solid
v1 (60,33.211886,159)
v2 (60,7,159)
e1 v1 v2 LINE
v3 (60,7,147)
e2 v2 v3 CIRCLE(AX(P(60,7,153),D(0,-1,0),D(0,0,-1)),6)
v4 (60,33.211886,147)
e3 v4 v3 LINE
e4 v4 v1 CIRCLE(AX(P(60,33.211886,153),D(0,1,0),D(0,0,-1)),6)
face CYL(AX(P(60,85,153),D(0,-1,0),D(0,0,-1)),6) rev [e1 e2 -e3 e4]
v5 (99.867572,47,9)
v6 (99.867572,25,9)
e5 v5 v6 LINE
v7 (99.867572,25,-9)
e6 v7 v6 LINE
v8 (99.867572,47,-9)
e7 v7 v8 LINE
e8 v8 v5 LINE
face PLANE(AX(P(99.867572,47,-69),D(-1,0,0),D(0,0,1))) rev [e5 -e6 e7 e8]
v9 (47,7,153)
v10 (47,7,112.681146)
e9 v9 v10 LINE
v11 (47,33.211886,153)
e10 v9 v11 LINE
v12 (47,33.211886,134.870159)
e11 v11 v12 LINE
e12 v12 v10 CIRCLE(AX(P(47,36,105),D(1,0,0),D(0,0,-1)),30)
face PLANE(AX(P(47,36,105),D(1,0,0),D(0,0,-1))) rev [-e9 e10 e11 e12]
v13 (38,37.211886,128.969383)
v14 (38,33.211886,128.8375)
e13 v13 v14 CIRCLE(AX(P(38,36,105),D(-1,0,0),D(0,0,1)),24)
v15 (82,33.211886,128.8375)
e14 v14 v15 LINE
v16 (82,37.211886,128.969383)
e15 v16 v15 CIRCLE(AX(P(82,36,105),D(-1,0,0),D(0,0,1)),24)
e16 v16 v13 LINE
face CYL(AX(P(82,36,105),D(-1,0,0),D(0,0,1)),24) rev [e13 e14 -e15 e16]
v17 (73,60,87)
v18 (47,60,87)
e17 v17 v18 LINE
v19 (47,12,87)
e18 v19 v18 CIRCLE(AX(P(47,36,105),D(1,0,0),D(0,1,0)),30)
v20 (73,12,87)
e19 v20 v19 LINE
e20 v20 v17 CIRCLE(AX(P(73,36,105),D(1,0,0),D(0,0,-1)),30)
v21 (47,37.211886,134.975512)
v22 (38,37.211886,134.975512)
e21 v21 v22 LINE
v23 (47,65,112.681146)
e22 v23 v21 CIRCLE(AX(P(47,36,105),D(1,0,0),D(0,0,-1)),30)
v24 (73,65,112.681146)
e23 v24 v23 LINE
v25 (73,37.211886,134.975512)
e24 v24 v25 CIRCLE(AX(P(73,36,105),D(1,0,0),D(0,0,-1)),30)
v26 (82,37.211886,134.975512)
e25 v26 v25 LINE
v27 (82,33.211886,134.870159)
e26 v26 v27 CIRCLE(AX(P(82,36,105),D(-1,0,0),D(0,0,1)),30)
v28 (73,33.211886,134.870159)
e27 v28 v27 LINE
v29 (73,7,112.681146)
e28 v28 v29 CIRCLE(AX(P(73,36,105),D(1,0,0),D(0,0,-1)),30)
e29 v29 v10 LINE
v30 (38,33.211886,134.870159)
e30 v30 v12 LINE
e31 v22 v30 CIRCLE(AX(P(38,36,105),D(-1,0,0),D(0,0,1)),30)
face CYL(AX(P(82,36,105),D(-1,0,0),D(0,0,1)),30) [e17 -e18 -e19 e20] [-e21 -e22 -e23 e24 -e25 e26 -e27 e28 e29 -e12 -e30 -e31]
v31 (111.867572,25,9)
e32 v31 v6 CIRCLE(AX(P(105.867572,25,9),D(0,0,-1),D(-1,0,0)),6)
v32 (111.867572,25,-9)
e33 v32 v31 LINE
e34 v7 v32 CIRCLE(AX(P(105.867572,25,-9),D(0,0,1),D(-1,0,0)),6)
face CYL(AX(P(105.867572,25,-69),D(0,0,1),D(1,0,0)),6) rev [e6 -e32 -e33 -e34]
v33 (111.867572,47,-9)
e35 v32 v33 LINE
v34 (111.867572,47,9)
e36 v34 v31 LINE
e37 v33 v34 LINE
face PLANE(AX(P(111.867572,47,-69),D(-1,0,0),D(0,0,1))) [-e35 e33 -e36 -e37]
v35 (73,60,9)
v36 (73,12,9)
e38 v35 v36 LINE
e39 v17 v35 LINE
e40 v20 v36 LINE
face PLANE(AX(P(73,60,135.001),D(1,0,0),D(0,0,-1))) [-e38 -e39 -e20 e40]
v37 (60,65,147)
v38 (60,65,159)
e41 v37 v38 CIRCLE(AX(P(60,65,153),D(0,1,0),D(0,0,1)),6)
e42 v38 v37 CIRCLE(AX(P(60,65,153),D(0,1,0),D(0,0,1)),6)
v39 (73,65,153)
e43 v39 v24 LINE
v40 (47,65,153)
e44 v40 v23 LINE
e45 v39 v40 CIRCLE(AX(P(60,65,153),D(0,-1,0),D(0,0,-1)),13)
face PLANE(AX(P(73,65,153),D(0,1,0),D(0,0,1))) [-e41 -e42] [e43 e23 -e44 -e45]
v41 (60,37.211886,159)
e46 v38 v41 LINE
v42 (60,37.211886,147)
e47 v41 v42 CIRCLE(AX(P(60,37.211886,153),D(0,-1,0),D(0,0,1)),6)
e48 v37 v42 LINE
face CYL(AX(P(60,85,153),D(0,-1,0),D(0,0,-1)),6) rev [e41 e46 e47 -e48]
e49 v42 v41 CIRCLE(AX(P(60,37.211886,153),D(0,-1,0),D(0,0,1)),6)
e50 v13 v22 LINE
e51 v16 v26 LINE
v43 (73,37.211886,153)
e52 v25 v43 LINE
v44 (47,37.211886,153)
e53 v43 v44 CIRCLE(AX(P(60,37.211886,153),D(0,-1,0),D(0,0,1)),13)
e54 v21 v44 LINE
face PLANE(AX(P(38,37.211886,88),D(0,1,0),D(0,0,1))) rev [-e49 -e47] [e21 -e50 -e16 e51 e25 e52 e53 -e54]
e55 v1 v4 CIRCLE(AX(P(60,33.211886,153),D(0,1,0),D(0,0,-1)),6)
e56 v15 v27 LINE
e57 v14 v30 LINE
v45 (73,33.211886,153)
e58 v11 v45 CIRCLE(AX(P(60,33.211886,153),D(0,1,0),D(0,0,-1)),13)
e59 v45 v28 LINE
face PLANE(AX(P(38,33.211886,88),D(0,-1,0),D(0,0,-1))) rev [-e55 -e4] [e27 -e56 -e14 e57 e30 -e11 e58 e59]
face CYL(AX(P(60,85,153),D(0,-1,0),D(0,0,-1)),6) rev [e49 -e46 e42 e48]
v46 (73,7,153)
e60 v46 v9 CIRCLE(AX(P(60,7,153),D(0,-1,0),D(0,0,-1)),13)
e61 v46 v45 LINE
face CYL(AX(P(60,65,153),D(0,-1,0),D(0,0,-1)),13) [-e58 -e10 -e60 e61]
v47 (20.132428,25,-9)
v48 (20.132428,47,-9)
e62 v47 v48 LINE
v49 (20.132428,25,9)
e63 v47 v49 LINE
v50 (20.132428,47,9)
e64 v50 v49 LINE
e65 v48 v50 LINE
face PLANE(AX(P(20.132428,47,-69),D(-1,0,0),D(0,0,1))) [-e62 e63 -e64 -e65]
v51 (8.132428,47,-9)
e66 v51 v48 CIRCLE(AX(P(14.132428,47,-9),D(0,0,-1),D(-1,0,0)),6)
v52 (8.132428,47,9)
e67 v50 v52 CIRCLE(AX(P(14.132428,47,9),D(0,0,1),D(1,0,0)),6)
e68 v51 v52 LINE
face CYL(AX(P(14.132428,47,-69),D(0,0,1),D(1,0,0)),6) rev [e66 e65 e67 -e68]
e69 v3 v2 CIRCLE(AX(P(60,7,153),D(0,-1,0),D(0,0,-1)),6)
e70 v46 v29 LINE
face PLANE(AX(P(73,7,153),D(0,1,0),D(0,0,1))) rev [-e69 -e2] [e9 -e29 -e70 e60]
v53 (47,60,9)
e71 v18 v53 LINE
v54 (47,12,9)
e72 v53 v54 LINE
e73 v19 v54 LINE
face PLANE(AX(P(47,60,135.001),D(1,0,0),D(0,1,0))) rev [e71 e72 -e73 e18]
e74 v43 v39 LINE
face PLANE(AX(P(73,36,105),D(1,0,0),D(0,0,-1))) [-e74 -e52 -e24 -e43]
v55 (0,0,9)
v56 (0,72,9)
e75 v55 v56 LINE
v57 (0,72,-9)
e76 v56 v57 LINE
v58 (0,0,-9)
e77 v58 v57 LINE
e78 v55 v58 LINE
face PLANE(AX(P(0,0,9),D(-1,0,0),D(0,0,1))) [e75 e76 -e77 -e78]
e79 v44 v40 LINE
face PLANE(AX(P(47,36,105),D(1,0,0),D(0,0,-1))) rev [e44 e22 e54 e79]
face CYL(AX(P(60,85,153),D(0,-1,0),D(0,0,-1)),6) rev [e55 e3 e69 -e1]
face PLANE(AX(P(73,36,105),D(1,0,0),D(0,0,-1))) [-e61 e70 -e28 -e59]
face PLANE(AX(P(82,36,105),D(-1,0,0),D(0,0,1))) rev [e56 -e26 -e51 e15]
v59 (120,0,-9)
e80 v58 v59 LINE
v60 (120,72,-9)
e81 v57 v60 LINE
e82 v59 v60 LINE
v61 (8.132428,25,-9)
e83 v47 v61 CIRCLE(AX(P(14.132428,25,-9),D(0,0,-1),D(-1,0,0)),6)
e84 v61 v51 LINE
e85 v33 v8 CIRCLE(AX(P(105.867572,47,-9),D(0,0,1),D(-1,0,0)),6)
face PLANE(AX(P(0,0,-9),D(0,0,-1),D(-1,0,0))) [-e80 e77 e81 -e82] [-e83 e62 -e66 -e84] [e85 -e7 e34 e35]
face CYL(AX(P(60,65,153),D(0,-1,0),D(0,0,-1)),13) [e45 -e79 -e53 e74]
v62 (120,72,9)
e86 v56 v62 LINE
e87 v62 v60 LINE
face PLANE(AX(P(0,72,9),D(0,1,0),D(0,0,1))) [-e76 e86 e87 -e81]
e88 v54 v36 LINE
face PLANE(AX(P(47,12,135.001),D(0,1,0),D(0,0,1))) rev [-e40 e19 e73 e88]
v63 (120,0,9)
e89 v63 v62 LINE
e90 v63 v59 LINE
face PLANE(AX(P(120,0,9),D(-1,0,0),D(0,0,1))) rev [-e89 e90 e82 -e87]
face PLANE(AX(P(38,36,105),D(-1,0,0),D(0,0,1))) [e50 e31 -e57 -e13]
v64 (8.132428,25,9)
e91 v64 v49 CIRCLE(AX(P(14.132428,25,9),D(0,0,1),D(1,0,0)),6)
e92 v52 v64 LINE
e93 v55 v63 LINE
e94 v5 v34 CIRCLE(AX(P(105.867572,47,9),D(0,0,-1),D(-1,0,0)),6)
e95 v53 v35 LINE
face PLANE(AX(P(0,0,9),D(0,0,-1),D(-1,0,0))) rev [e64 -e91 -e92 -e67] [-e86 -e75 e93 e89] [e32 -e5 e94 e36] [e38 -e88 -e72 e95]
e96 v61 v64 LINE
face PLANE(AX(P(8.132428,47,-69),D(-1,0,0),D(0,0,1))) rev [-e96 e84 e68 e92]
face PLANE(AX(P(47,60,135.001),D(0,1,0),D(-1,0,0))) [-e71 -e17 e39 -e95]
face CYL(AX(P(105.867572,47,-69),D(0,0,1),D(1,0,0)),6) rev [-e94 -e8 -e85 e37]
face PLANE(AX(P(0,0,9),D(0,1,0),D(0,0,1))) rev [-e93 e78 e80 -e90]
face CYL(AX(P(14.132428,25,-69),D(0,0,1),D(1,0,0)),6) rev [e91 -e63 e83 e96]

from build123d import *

# Parameters (mm, degrees)
BASE_PLATE_SKETCH_W        = 120
BASE_PLATE_SKETCH_H        = 72
BASE_PLATE_120X72X18_DEPTH = 9
CLAMP_RING_SKETCH_R        = 30
CLAMP_RING_SKETCH_R_2      = 24
CLAMP_RING_DEPTH           = 22
ARM_REACH                  = 190.308
ARM_END_RADIUS             = 30
ARM_PROFILE_SKETCH_W       = 26
ARM_PROFILE_SKETCH_H       = 48
CLAMP_LUG_DEPTH            = 13
CLAMP_LUG_EXTENSION_DEPTH  = 58
CLAMP_BOLT_HOLE_SKETCH_R   = 6
CLAMP_BOLT_HOLE_12_DEPTH   = 78
CLAMP_SPLIT_SLOT_SKETCH_W  = 44
CLAMP_SPLIT_SLOT_SKETCH_H  = 4
CLAMP_SPLIT_SLOT_4MM_DEPTH = 78
MOUNTING_SLOTS_2X_DEPTH    = 78


with BuildPart() as part:
    # Base Plate Sketch → Base Plate 120x72x18 (new, symmetric)
    with BuildSketch(Plane.XY):
        with Locations((60, 36)):
            Rectangle(BASE_PLATE_SKETCH_W, BASE_PLATE_SKETCH_H)
    extrude(amount=BASE_PLATE_120X72X18_DEPTH, both=True)



with BuildPart() as body_2:
    # Clamp Ring Sketch → Clamp Ring (new, symmetric)
    with BuildSketch(Plane(origin=(60, 0, 0), x_dir=(0, 0, -1), z_dir=(1, 0, 0))):
        with Locations(Location((-105, 36, 0), (0, 0, 180))):
            Circle(CLAMP_RING_SKETCH_R)
        with Locations(Location((-105, 36, 0), (0, 0, 180))):
            Circle(CLAMP_RING_SKETCH_R_2, mode=Mode.SUBTRACT)
    extrude(amount=CLAMP_RING_DEPTH, both=True)


with BuildPart() as part_1:
    add(part.part)

    add(body_2.part)  # Arm merges body 2
    # Arm: up to this cylinder (the profile starts outside it)
    arm_end = Plane(origin=(60, 36, 105), z_dir=(-1, 0, 0)) * Cylinder(ARM_END_RADIUS, 441.616, mode=Mode.PRIVATE)
    # Arm Profile Sketch → Arm (add, up to the surface)
    with BuildSketch(Plane.XY.offset(9), mode=Mode.PRIVATE) as arm_sk1:
        with Locations((60, 36)):
            Rectangle(ARM_PROFILE_SKETCH_W, ARM_PROFILE_SKETCH_H)
    arm_tool1 = extrude(arm_sk1.sketch, amount=ARM_REACH, mode=Mode.PRIVATE) - arm_end
    add(arm_tool1.solids().sort_by_distance((60, 36, 9))[0])

    # Clamp Lug Sketch → Clamp Lug (add, symmetric)
    with BuildSketch(Plane(origin=(60, 0, 0), x_dir=(0, 0, -1), z_dir=(1, 0, 0))):
        with BuildLine():
            Line((-153, 7), (-153, 65))
            Line((-153, 65), (-112.681145748, 65))
            ThreePointArc((-112.681145748, 65), (-135, 36), (-112.681145748, 7))
            Line((-112.681145748, 7), (-153, 7))
        make_face()
    extrude(amount=CLAMP_LUG_DEPTH, both=True)

    # Clamp Lug Extension Sketch → Clamp Lug Extension (add)
    with BuildSketch(Plane.XZ.offset(-7)):
        with BuildLine():
            Line((47, 153), (73, 153))
            ThreePointArc((73, 153), (60, 166), (47, 153))
        make_face()
    extrude(amount=-CLAMP_LUG_EXTENSION_DEPTH)

    # Clamp Bolt Hole Sketch → Clamp Bolt Hole Ø12 (cut)
    with BuildSketch(Plane.XZ.offset(-7)):
        with Locations(Location((60, 153, 0), (0, 0, 270))):
            Circle(CLAMP_BOLT_HOLE_SKETCH_R)
    extrude(amount=-CLAMP_BOLT_HOLE_12_DEPTH, mode=Mode.SUBTRACT)

    # Clamp Split Slot Sketch → Clamp Split Slot 4mm (cut)
    with BuildSketch(Plane.XY.offset(166)):
        with Locations((60, 35.211886187)):
            Rectangle(CLAMP_SPLIT_SLOT_SKETCH_W, CLAMP_SPLIT_SLOT_SKETCH_H)
    extrude(amount=-CLAMP_SPLIT_SLOT_4MM_DEPTH, mode=Mode.SUBTRACT)

    # Mounting Slots Sketch → Mounting Slots 2x (cut)
    with BuildSketch(Plane.XY.offset(9)):
        with BuildLine():
            Line((20.132428188, 47), (20.132428188, 25))
            ThreePointArc((20.132428188, 25), (14.132428188, 19), (8.132428188, 25))
            Line((8.132428188, 25), (8.132428188, 47))
            ThreePointArc((8.132428188, 47), (14.132428188, 53), (20.132428188, 47))
        make_face()
        with BuildLine():
            Line((99.867571812, 47), (99.867571812, 25))
            ThreePointArc((99.867571812, 25), (105.867571812, 19), (111.867571812, 25))
            Line((111.867571812, 25), (111.867571812, 47))
            ThreePointArc((111.867571812, 47), (105.867571812, 53), (99.867571812, 47))
        make_face()
    extrude(amount=-MOUNTING_SLOTS_2X_DEPTH, mode=Mode.SUBTRACT)


solid = part_1.part
